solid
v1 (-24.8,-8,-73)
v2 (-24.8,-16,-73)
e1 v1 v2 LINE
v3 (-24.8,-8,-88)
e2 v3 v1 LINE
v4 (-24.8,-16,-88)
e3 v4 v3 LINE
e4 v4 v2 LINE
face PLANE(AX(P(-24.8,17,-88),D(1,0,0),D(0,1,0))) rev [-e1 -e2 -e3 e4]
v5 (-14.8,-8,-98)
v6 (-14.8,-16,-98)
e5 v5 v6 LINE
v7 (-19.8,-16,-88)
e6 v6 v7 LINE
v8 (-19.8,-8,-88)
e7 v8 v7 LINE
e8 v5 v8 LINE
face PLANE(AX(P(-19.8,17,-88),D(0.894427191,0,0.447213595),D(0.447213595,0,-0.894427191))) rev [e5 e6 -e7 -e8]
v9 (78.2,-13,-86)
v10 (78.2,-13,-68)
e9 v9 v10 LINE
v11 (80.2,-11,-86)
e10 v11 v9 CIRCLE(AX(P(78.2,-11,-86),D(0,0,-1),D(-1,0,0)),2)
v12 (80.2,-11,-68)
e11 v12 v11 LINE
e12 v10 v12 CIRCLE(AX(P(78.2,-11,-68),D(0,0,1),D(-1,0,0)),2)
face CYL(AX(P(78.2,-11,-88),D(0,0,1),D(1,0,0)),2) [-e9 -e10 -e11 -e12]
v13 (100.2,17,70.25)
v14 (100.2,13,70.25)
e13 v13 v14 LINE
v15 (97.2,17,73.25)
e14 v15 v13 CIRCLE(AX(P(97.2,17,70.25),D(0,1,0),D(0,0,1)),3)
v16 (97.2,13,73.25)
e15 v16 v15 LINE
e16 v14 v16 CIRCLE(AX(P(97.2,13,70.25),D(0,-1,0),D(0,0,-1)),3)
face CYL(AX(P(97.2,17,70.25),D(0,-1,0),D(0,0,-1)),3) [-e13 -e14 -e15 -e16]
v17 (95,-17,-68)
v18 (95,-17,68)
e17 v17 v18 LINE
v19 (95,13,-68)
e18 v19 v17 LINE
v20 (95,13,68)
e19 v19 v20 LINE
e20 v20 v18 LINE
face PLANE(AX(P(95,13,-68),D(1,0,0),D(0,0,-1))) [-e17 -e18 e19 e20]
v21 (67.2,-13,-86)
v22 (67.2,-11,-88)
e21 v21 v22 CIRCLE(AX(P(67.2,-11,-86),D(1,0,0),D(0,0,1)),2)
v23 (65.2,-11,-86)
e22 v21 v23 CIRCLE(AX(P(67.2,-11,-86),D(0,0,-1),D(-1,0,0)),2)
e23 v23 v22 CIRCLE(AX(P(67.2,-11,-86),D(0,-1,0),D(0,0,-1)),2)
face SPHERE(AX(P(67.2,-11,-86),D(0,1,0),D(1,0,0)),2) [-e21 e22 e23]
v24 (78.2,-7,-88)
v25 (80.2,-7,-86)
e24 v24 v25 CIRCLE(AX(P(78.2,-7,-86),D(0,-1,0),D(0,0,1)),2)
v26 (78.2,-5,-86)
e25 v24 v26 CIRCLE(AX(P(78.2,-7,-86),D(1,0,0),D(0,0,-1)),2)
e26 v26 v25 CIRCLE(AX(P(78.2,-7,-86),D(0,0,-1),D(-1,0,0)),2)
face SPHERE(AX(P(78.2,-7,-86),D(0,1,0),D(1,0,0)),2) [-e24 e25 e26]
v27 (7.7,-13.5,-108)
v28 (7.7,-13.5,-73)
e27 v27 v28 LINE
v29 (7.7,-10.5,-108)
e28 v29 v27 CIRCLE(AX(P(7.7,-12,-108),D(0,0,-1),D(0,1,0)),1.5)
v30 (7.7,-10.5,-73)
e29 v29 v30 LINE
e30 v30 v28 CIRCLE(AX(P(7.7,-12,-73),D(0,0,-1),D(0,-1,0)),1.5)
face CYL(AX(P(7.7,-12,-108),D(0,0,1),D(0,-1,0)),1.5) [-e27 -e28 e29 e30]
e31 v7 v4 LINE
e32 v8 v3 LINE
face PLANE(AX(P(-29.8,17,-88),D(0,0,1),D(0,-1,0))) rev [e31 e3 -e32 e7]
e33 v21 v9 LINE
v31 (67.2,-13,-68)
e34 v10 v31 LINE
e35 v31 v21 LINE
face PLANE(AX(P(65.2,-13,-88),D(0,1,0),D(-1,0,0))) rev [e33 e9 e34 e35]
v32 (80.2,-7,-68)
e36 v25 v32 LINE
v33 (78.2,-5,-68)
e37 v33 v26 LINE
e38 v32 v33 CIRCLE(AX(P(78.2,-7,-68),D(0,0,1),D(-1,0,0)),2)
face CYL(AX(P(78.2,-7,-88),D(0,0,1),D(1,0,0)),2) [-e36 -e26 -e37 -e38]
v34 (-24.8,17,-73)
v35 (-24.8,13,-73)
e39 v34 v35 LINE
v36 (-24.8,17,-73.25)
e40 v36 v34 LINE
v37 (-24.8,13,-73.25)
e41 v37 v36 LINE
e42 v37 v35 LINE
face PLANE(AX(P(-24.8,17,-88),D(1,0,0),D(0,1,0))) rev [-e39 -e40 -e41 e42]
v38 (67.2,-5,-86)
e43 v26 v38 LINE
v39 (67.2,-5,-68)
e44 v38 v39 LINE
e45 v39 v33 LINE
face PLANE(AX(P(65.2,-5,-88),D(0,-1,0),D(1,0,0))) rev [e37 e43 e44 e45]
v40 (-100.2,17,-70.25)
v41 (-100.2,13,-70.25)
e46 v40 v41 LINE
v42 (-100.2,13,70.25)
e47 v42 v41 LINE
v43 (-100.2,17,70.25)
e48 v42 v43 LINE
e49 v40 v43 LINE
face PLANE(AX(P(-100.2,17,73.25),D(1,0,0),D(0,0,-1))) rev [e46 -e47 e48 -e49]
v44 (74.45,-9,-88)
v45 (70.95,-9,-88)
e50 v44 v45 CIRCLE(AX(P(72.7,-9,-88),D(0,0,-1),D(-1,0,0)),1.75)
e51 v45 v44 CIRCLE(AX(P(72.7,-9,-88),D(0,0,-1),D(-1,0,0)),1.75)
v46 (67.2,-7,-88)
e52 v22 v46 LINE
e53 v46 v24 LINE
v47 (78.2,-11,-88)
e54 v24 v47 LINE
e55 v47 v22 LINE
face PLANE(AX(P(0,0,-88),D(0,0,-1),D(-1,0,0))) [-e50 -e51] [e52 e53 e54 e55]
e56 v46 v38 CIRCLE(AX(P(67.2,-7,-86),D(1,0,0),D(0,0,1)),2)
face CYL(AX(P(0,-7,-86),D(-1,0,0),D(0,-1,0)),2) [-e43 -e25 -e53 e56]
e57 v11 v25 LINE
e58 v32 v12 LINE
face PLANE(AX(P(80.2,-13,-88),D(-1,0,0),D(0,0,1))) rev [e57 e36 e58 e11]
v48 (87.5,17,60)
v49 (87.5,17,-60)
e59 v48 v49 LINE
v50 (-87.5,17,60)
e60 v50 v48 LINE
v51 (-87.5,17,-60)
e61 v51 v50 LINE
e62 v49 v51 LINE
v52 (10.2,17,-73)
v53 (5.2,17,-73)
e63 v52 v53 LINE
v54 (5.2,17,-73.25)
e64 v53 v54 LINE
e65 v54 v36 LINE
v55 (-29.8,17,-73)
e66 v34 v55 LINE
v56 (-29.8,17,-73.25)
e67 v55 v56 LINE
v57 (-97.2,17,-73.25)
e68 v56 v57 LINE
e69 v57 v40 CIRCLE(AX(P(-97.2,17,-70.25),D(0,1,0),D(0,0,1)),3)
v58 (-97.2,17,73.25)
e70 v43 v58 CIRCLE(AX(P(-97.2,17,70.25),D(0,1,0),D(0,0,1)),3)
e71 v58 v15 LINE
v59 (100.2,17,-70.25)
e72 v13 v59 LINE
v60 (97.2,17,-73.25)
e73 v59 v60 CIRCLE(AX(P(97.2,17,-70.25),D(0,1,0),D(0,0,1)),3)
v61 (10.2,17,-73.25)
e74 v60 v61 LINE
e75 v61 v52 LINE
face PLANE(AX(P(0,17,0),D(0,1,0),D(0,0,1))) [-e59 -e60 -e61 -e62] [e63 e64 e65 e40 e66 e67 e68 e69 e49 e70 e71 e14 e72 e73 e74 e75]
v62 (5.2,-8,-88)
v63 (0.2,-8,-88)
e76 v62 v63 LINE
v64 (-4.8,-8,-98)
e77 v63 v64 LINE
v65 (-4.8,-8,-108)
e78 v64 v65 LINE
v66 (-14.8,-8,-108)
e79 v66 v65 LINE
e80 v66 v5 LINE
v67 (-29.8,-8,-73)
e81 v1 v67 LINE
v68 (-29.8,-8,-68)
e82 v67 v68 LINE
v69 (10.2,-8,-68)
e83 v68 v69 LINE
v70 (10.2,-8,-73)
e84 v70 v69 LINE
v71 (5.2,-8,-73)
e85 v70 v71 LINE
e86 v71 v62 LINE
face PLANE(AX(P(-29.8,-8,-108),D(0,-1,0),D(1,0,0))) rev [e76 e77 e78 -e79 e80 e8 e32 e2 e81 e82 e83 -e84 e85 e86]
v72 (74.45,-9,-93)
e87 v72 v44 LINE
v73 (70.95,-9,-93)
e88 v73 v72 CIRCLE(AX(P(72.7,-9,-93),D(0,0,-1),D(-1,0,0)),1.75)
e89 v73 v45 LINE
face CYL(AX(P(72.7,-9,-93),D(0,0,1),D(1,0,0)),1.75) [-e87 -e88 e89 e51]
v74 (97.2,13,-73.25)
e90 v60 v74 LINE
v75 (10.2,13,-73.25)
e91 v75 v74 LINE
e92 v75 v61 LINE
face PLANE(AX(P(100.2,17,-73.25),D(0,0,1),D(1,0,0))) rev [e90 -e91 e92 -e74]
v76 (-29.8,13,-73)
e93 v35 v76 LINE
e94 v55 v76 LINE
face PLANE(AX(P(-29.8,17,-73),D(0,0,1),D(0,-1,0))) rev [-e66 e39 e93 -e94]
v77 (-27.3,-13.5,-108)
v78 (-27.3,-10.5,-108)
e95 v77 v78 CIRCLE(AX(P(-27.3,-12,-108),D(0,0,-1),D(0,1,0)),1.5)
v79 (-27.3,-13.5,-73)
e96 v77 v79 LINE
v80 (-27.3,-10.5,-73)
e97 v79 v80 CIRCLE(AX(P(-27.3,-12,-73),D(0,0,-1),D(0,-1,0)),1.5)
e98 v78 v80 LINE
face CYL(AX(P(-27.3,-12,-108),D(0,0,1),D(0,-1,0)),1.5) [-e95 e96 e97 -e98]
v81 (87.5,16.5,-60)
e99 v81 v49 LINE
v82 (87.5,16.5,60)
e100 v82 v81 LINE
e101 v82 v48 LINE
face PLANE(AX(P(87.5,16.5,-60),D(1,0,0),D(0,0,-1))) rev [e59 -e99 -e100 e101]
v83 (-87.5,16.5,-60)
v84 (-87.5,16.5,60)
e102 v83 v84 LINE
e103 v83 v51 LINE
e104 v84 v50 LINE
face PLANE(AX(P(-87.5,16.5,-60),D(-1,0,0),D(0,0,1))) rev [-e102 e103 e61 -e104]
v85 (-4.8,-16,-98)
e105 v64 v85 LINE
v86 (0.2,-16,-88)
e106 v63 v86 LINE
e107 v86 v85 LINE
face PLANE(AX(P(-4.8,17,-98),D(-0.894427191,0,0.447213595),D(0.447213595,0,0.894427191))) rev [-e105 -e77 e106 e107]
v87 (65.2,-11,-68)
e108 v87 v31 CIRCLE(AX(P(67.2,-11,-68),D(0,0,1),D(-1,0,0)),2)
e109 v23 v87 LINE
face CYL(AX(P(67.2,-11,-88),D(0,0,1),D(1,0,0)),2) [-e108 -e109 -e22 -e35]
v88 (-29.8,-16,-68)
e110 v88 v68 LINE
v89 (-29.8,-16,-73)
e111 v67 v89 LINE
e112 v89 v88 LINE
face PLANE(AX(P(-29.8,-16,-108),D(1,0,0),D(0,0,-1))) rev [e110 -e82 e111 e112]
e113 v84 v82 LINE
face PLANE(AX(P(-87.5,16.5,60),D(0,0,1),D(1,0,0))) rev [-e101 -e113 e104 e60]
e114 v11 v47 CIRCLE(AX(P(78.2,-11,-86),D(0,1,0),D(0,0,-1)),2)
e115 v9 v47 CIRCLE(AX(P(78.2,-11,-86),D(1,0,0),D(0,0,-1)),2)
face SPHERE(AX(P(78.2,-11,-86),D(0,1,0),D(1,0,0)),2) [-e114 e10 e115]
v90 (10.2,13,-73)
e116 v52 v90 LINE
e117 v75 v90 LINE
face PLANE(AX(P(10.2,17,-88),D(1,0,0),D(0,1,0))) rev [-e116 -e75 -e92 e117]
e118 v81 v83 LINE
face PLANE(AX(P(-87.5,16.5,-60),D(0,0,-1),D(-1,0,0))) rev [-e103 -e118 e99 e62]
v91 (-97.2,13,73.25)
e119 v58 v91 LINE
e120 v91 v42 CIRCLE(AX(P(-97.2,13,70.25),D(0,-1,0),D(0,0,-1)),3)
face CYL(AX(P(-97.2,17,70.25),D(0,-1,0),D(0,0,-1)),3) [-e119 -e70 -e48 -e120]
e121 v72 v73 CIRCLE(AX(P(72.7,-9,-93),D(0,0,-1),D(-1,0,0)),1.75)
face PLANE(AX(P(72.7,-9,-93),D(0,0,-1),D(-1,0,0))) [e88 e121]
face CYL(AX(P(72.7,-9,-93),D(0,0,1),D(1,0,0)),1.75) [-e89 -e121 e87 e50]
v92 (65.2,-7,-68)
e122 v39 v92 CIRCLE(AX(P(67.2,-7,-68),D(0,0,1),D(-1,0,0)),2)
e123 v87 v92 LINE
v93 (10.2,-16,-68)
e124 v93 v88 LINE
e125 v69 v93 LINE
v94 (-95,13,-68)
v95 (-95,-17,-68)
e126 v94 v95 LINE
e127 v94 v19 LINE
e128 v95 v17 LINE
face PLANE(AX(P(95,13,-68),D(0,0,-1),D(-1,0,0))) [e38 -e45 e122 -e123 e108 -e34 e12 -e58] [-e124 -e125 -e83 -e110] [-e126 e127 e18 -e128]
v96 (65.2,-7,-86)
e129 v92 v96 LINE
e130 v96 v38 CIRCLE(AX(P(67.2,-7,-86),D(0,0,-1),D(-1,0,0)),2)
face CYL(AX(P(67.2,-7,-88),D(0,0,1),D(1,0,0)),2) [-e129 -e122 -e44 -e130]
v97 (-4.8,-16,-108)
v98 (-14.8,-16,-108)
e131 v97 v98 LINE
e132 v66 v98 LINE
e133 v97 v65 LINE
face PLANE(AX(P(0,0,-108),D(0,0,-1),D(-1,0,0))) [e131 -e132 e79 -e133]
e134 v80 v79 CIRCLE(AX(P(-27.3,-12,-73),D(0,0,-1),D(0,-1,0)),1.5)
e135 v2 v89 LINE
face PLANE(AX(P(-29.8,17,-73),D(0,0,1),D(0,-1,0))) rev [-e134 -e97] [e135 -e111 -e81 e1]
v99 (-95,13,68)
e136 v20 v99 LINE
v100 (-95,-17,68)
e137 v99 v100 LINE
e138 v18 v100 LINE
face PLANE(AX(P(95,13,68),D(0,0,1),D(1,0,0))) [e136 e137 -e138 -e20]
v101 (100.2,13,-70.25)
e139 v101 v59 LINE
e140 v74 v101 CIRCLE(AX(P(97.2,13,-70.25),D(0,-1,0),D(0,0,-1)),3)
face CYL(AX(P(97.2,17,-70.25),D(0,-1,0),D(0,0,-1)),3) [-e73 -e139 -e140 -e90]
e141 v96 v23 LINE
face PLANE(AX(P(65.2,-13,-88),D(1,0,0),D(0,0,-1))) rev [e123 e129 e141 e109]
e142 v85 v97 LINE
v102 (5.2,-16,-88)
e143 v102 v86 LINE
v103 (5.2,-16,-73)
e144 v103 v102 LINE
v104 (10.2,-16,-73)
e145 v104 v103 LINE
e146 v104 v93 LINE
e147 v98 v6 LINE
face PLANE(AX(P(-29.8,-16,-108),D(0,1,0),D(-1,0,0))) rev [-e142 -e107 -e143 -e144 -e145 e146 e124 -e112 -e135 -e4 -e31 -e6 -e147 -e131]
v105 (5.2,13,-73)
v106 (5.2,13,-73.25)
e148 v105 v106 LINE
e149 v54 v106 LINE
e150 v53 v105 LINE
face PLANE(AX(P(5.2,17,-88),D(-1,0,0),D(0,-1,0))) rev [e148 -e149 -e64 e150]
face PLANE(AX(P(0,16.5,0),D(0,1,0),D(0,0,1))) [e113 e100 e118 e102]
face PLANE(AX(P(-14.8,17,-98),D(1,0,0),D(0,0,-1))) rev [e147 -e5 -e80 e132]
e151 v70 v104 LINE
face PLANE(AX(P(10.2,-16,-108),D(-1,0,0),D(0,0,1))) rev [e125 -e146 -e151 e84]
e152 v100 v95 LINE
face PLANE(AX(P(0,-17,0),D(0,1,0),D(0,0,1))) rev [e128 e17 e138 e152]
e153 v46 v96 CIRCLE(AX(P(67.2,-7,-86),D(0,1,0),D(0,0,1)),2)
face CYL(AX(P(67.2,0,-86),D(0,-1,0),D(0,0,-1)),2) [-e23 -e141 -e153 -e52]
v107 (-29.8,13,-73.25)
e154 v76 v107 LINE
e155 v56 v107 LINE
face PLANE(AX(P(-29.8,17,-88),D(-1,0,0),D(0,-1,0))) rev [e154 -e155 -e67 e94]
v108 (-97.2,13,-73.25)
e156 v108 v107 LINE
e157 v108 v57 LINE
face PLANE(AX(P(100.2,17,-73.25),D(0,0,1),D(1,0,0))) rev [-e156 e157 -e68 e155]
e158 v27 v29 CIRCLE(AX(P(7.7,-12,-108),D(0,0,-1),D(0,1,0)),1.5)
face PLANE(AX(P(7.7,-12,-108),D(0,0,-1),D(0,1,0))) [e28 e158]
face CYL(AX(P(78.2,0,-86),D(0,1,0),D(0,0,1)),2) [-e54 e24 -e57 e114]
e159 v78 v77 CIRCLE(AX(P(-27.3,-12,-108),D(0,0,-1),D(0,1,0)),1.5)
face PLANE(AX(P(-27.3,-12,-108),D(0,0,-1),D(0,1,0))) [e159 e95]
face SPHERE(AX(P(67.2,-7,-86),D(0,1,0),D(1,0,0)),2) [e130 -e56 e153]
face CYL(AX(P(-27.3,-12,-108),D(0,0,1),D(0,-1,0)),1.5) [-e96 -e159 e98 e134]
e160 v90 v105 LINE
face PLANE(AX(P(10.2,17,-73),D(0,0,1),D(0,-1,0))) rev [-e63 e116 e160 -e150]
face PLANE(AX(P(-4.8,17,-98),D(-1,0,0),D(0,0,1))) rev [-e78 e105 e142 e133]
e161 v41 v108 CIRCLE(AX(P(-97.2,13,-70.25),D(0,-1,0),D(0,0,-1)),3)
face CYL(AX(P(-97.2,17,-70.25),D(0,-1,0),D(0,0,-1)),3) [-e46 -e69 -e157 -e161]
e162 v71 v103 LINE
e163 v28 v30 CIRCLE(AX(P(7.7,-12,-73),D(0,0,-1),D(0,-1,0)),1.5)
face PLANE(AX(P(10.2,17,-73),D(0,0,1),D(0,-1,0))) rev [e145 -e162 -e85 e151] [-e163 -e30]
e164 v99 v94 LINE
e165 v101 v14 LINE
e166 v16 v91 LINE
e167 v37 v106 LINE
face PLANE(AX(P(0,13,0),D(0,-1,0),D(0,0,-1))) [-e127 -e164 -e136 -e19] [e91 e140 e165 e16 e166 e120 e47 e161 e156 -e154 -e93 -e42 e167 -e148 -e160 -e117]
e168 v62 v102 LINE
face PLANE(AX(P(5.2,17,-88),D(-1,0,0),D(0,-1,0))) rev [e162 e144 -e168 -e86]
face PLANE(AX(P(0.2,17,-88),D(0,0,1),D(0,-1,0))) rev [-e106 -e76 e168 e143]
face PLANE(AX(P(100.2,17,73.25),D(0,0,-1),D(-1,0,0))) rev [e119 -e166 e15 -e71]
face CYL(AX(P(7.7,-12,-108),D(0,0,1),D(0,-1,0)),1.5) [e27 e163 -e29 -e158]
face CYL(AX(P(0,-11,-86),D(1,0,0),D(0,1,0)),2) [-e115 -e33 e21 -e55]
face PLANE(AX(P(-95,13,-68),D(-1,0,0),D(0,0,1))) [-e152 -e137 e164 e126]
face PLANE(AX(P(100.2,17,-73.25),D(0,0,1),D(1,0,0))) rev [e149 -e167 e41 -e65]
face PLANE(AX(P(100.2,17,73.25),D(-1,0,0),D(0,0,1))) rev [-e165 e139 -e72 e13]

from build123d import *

# Parameters (mm, degrees)
SKETCH_1_W          = 200.4
SKETCH_1_H          = 146.5
EXTRUDE_1_DEPTH     = 17
SKETCH_2_W          = 175
SKETCH_2_H          = 120
CUT_EXTRUDE_1_DEPTH = 0.5
SKETCH_3_W          = 200.4
SKETCH_3_H          = 146.5
SKETCH_3_W_2        = 190
SKETCH_3_H_2        = 136
CUT_EXTRUDE_2_DEPTH = 30
FILLET_1_R          = 3
SKETCH_4_W          = 40
SKETCH_4_H          = 8
EXTRUDE_2_DEPTH     = 40
SKETCH_5_W          = 15
SKETCH_5_H          = 8
EXTRUDE_3_DEPTH     = 20
FILLET_2_R          = 2
SKETCH_6_R          = 1.75
EXTRUDE_4_DEPTH     = 5
CUT_EXTRUDE_3_DEPTH = 151.973640083
SKETCH_8_W          = 5
SKETCH_8_H          = 15
CUT_EXTRUDE_4_DEPTH = 151.973640083
SKETCH_9_R          = 1.5
EXTRUDE_5_DEPTH     = 35


with BuildPart() as part:
    # 草图1 → 凸台-拉伸1 (new, symmetric)
    with BuildSketch(Plane(origin=(0, 0, 0), x_dir=(1, 0, 0), z_dir=(0, 1, 0))):
        Rectangle(SKETCH_1_W, SKETCH_1_H)
    extrude(amount=EXTRUDE_1_DEPTH, both=True)

    # 草图2 → 切除-拉伸1 (cut)
    with BuildSketch(Plane(origin=(0, 17, 0), x_dir=(1, 0, 0), z_dir=(0, 1, 0))):
        Rectangle(SKETCH_2_W, SKETCH_2_H)
    extrude(amount=-CUT_EXTRUDE_1_DEPTH, mode=Mode.SUBTRACT)

    # 草图3 → 切除-拉伸2 (cut)
    with BuildSketch(Plane.XZ.offset(17)):
        Rectangle(SKETCH_3_W, SKETCH_3_H)
        Rectangle(SKETCH_3_W_2, SKETCH_3_H_2, mode=Mode.SUBTRACT)
    extrude(amount=-CUT_EXTRUDE_2_DEPTH, mode=Mode.SUBTRACT)

    # 圆角1
    fillet_1_edges = [part.edges().sort_by_distance(p)[0] for p in [
        (-100.2, 15, -73.25),
        (100.2, 15, -73.25),
        (100.2, 15, 73.25),
        (-100.2, 15, 73.25),
    ]]
    fillet(fillet_1_edges, radius=FILLET_1_R)

    # 草图4 → 凸台-拉伸2 (add)
    with BuildSketch(Plane(origin=(0, 0, -68), x_dir=(-1, 0, 0), z_dir=(0, 0, -1))):
        with Locations((9.8, -12)):
            Rectangle(SKETCH_4_W, SKETCH_4_H)
    extrude(amount=EXTRUDE_2_DEPTH)

    # 草图5 → 凸台-拉伸3 (add)
    with BuildSketch(Plane(origin=(0, 0, -68), x_dir=(-1, 0, 0), z_dir=(0, 0, -1))):
        with Locations((-72.7, -9)):
            Rectangle(SKETCH_5_W, SKETCH_5_H)
    extrude(amount=EXTRUDE_3_DEPTH)

    # 圆角2
    fillet_2_edges = [part.edges().sort_by_distance(p)[0] for p in [
        (65.2, -13, -78),
        (65.2, -5, -78),
        (80.2, -5, -78),
        (80.2, -13, -78),
        (65.2, -9, -88),
        (72.7, -5, -88),
        (80.2, -9, -88),
        (72.7, -13, -88),
    ]]
    fillet(fillet_2_edges, radius=FILLET_2_R)

    # 草图6 → 凸台-拉伸4 (add)
    with BuildSketch(Plane(origin=(0, 0, -88), x_dir=(-1, 0, 0), z_dir=(0, 0, -1))):
        with Locations((-72.7, -9)):
            Circle(SKETCH_6_R)
    extrude(amount=EXTRUDE_4_DEPTH)

    # 草图7 → 切除-拉伸3 (cut, through all)
    with BuildSketch(Plane.XZ.offset(16)):
        Polygon((-29.8, -88), (-19.8, -88), (-14.8, -98), (-14.8, -108), (-29.8, -108), align=None)
        Polygon((-4.8, -98), (-4.8, -108), (10.2, -108), (10.2, -88), (0.2, -88), align=None)
    extrude(amount=-CUT_EXTRUDE_3_DEPTH, mode=Mode.SUBTRACT)

    # 草图8 → 切除-拉伸4 (cut, through all)
    with BuildSketch(Plane.XZ.offset(16)):
        with Locations((-27.3, -80.5)):
            Rectangle(SKETCH_8_W, SKETCH_8_H)
        with Locations((7.7, -80.5)):
            Rectangle(SKETCH_8_W, SKETCH_8_H)
    extrude(amount=-CUT_EXTRUDE_4_DEPTH, mode=Mode.SUBTRACT)

    # 草图9 → 凸台-拉伸5 (add)
    with BuildSketch(Plane(origin=(0, 0, -73), x_dir=(-1, 0, 0), z_dir=(0, 0, -1))):
        with Locations(Location((27.3, -12, 0), (0, 0, 270))):
            Circle(SKETCH_9_R)
        with Locations(Location((-7.7, -12, 0), (0, 0, 270))):
            Circle(SKETCH_9_R)
    extrude(amount=EXTRUDE_5_DEPTH)


solid = part.part
